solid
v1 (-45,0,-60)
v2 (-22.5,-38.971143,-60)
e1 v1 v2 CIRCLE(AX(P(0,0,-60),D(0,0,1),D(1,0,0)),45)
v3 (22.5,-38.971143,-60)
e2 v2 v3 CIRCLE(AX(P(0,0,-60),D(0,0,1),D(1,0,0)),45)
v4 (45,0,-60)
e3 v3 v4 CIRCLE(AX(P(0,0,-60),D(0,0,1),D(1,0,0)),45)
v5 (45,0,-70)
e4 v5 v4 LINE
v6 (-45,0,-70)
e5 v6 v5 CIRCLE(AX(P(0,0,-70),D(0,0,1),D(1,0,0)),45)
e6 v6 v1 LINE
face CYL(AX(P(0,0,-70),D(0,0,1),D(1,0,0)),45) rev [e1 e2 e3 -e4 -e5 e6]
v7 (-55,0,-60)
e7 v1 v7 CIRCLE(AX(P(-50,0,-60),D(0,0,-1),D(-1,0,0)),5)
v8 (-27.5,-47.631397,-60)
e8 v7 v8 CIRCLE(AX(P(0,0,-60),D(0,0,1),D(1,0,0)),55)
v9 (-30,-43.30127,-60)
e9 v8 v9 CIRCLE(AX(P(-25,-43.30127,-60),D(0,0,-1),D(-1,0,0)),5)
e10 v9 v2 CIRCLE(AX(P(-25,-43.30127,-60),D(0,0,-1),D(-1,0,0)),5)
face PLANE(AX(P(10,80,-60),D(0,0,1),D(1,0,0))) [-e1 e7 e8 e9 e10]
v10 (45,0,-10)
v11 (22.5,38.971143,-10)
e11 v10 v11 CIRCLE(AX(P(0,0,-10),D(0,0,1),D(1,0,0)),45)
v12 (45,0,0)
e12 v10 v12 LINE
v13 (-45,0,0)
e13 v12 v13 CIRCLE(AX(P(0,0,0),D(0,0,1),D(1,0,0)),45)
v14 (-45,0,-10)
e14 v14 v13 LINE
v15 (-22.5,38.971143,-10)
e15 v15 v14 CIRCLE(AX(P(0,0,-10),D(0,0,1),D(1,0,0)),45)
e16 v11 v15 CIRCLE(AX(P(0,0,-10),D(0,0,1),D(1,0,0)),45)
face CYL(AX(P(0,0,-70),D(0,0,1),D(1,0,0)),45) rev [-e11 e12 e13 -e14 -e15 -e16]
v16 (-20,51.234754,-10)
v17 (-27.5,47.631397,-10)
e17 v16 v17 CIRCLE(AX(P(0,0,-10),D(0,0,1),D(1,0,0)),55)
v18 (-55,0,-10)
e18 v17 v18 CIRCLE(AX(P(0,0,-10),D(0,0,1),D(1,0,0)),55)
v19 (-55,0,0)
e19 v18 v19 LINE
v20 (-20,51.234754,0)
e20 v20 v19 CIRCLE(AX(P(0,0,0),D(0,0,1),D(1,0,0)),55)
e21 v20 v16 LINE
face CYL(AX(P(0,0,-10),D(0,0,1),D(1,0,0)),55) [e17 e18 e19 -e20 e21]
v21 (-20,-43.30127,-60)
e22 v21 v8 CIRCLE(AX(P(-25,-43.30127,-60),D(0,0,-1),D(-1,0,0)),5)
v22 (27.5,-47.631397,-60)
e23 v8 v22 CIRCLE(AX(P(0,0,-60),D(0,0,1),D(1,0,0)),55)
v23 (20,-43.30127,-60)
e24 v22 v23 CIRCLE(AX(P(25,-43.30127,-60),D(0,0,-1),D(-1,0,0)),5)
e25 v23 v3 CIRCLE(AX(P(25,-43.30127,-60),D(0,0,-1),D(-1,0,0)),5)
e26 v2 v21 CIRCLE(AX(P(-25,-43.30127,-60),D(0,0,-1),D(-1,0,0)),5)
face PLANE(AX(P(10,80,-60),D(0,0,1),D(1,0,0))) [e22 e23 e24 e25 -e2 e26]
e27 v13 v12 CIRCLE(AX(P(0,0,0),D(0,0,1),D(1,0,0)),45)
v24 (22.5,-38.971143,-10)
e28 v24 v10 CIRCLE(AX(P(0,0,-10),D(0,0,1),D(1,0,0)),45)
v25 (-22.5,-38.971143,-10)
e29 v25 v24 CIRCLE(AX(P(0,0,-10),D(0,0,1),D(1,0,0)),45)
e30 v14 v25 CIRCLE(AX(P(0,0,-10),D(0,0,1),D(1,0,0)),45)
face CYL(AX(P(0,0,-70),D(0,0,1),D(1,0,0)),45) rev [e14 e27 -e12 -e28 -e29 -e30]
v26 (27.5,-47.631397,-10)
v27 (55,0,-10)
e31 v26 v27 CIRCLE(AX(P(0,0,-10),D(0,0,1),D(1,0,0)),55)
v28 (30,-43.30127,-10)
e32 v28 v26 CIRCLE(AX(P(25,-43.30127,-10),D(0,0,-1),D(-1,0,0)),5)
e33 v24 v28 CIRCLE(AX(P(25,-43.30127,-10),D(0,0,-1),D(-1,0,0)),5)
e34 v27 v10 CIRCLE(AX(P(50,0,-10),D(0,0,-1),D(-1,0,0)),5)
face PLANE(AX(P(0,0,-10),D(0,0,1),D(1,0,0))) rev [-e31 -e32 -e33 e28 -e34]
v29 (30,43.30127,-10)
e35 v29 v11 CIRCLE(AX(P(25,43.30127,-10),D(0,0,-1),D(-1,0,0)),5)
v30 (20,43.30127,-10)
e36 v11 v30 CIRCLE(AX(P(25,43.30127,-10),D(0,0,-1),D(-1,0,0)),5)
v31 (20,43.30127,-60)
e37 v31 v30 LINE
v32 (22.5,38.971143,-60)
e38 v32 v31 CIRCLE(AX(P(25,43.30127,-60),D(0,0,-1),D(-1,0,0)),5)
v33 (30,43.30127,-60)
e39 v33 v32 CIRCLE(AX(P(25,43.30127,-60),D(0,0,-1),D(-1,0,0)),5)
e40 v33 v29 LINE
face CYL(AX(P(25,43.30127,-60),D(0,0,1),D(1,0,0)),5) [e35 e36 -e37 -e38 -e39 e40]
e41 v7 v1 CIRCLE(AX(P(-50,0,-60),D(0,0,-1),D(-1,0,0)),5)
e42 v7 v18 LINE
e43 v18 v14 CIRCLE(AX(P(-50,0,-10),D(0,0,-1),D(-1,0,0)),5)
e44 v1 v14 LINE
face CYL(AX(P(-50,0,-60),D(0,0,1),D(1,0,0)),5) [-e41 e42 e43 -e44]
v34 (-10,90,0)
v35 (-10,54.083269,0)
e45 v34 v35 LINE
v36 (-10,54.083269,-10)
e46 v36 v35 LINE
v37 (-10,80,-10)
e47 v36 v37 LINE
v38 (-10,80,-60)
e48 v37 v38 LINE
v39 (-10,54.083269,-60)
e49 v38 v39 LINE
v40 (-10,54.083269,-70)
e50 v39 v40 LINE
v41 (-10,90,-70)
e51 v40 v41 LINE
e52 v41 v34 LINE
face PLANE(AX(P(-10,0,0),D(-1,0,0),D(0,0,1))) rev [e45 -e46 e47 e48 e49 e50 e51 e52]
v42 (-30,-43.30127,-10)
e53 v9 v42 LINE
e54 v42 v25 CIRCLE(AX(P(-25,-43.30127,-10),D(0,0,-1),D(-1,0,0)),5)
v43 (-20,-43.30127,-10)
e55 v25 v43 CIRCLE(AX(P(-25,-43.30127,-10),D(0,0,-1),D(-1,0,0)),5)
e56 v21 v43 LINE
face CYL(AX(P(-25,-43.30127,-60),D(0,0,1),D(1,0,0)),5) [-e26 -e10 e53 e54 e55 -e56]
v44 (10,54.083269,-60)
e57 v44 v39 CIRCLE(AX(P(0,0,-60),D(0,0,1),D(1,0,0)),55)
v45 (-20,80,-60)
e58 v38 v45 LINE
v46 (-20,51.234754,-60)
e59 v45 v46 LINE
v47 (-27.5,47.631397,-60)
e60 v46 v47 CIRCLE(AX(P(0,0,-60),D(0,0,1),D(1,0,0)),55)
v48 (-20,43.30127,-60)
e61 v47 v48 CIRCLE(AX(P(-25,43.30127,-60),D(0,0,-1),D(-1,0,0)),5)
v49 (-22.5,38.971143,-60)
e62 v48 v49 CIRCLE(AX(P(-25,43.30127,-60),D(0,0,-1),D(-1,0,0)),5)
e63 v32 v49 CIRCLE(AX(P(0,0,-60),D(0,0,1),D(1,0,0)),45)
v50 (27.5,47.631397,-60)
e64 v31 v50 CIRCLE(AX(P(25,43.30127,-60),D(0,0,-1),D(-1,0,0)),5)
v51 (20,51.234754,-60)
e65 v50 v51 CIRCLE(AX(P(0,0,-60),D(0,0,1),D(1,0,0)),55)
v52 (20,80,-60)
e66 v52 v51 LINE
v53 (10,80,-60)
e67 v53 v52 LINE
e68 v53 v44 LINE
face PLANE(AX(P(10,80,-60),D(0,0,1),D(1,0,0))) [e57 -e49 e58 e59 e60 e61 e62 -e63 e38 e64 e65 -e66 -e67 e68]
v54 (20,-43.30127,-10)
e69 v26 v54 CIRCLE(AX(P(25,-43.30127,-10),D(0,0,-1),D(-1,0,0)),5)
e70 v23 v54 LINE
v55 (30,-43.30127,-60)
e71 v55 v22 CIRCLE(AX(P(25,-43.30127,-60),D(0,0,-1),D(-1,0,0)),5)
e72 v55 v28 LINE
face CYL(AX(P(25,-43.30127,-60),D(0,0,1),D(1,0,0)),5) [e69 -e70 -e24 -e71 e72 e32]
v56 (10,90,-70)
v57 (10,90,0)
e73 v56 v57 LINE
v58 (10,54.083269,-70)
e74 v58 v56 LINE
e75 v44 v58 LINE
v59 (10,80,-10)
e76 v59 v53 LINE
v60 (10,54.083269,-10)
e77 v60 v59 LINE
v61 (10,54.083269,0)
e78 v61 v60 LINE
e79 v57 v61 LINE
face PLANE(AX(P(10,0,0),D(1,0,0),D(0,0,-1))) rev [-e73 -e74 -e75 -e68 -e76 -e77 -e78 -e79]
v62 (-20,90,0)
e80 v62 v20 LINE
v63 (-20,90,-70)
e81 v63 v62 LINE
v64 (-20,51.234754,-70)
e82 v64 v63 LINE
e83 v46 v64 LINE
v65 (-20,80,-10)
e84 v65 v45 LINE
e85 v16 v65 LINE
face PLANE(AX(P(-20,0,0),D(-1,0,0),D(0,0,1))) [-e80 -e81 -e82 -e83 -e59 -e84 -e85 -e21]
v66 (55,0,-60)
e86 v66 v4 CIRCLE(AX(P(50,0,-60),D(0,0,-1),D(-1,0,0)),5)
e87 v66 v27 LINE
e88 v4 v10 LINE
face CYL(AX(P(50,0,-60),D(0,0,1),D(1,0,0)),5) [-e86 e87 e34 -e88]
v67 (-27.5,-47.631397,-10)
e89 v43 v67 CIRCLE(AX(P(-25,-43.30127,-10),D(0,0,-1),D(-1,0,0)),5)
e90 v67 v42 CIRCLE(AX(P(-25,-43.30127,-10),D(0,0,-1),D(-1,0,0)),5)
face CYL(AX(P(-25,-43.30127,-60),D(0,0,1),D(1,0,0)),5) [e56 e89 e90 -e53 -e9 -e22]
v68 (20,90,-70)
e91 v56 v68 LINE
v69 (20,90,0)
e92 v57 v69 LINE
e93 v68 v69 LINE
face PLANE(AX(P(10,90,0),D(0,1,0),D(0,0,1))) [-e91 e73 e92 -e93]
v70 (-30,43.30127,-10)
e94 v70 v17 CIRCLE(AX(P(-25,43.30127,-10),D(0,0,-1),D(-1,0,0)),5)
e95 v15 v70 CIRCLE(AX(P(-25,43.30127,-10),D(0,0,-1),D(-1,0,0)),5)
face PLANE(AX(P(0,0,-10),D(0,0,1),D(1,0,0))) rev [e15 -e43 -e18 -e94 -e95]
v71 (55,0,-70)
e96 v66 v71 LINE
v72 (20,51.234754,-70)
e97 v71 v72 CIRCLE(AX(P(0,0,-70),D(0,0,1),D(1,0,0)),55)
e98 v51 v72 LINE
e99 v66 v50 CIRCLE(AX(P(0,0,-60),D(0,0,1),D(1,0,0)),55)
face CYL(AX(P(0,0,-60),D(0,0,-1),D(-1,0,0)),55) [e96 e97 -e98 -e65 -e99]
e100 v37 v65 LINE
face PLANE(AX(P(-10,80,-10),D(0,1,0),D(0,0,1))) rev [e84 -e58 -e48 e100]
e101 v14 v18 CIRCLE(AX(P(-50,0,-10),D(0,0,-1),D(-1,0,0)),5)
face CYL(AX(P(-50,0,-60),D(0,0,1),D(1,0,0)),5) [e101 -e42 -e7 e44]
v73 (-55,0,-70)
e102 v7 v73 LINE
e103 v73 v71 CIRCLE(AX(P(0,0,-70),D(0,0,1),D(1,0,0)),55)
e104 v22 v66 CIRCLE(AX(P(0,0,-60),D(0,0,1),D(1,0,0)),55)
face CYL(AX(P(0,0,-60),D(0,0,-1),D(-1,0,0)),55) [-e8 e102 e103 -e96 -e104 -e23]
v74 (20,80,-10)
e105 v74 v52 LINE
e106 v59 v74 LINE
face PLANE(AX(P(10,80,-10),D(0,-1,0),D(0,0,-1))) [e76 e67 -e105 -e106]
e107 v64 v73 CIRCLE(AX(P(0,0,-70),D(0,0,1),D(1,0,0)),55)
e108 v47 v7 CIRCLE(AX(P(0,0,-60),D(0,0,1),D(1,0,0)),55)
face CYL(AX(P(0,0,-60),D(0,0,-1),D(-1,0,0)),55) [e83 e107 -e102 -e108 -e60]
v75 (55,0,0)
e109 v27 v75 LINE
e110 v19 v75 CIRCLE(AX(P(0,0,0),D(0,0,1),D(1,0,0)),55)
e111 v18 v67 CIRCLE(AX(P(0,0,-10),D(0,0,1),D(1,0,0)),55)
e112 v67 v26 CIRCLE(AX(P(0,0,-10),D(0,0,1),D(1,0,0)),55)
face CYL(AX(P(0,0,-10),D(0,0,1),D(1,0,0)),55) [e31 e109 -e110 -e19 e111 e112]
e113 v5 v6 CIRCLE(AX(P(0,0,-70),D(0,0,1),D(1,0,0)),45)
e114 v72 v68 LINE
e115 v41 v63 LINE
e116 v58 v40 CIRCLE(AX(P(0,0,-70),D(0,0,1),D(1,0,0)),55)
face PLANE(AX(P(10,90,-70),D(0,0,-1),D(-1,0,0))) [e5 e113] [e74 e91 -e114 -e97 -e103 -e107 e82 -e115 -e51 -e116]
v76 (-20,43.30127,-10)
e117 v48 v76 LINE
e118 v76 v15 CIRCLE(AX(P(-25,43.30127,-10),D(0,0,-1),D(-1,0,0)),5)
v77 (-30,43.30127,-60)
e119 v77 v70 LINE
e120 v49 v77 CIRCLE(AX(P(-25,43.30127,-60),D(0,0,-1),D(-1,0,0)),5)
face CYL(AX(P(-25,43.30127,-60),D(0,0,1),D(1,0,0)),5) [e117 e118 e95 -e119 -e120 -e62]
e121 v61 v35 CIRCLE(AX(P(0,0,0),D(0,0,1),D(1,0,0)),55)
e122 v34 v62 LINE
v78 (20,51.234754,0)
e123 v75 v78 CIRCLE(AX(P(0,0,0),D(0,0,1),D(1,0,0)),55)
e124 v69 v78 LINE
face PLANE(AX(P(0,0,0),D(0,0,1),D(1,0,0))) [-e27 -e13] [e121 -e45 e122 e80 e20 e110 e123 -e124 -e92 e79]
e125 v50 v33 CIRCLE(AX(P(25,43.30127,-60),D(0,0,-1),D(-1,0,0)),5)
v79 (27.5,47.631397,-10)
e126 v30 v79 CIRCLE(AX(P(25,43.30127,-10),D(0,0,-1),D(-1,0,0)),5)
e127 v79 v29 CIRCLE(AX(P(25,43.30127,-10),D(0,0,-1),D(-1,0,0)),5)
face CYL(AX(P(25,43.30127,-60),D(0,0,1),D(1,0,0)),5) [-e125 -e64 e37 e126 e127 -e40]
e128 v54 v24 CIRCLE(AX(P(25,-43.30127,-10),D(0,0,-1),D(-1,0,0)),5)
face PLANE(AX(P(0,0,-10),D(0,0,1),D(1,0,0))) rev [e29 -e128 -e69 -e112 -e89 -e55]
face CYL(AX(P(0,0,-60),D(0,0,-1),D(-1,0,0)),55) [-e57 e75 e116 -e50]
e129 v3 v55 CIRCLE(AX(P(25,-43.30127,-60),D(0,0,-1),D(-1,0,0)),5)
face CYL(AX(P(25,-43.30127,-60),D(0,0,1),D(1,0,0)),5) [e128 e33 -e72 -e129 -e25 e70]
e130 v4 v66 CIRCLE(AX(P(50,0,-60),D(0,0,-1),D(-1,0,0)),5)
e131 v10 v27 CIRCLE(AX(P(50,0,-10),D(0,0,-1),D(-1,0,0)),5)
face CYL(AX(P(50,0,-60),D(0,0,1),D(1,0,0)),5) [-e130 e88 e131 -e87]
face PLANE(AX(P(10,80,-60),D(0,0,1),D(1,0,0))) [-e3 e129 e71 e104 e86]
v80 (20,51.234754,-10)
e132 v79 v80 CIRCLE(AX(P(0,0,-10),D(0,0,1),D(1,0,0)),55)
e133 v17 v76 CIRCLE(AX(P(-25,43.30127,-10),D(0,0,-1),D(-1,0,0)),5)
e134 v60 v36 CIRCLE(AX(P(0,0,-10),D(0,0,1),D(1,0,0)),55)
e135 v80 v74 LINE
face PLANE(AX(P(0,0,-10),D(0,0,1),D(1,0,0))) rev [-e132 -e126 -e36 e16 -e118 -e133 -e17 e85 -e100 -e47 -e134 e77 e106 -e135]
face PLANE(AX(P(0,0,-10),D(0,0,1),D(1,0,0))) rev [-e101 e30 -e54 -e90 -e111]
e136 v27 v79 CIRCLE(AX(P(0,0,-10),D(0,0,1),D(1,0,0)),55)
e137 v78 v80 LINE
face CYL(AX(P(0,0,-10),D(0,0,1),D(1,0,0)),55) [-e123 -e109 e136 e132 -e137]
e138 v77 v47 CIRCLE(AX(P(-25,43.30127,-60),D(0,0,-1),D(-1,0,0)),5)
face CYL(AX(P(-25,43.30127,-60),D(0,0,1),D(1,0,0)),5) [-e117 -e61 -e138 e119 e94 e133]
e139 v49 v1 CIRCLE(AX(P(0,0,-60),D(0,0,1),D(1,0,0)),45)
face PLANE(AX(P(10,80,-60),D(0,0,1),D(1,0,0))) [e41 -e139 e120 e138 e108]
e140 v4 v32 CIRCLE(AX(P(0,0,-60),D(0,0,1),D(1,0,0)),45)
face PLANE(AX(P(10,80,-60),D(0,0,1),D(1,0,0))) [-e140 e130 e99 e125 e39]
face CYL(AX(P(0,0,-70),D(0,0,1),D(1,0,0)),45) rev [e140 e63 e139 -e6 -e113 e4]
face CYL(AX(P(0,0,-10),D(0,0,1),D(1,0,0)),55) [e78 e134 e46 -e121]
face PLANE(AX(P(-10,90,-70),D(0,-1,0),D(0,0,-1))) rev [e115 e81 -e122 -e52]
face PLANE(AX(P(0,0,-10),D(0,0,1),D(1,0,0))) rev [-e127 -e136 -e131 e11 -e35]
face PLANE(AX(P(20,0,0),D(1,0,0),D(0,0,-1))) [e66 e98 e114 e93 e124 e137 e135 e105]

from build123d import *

# Parameters (mm, degrees)
FRONT_RING_PROFILE_110_R  = 55
FRONT_RING_DISC_DEPTH     = 10
REAR_RING_PROFILE_R       = 55
REAR_RING_DISC_DEPTH      = 10
RING_BORE_90_PROFILE_R    = 45
RING_BORE_90_DEPTH        = 105.642247682
FRONT_CLAMP_BRACKET_DEPTH = 10
REAR_CLAMP_BRACKET_DEPTH  = 10
CAGE_RODS_6X_10_PROFILE_R = 5
CAGE_RODS_6X_10_DEPTH     = 50


with BuildPart() as part:
    # Front Ring Profile Ø110 → Front Ring Disc (new body)
    with BuildSketch(Plane.XY):
        Circle(FRONT_RING_PROFILE_110_R)
    extrude(amount=-FRONT_RING_DISC_DEPTH)


with BuildPart() as body_2:
    # Rear Ring Profile → Rear Ring Disc (new body)
    with BuildSketch(Plane.XY.offset(-70)):
        Circle(REAR_RING_PROFILE_R)
    extrude(amount=REAR_RING_DISC_DEPTH)


with BuildPart() as ring_bore_90_tool:
    # Ring Bore Ø90 Profile → Ring Bore Ø90 (new, through all)
    with BuildSketch(Plane.XY):
        Circle(RING_BORE_90_PROFILE_R)
    extrude(amount=-RING_BORE_90_DEPTH)


with BuildPart() as part_1:
    add(part.part)

    # Ring Bore Ø90: cut by ring_bore_90_tool
    add(ring_bore_90_tool.part, mode=Mode.SUBTRACT)



with BuildPart() as body_2_1:
    add(body_2.part)

    # Ring Bore Ø90: cut by ring_bore_90_tool
    add(ring_bore_90_tool.part, mode=Mode.SUBTRACT)


with BuildPart() as part_2:
    add(part_1.part)

    add(body_2_1.part)  # Front Clamp Bracket merges body 2
    # Front Clamp Bracket Profile → Front Clamp Bracket (add)
    with BuildSketch(Plane(origin=(20, 0, 0), x_dir=(0, 0, -1), z_dir=(1, 0, 0))):
        Polygon((0, 45), (0, 90), (70, 90), (70, 45), (60, 45), (60, 80), (10, 80), (10, 45), align=None)
    extrude(amount=-FRONT_CLAMP_BRACKET_DEPTH)

    # Rear Clamp Bracket Profile → Rear Clamp Bracket (add)
    with BuildSketch(Plane(origin=(-20, 0, 0), x_dir=(0, 0, -1), z_dir=(1, 0, 0))):
        Polygon((10, 80), (60, 80), (60, 51.23475383), (70, 51.23475383), (70, 90), (0, 90), (0, 51.23475383), (10, 51.23475383), align=None)
    extrude(amount=REAR_CLAMP_BRACKET_DEPTH)

    # Cage Rods 6xØ10 Profile → Cage Rods 6xØ10 (add)
    with BuildSketch(Plane(origin=(0, 0, -10), x_dir=(-1, 0, 0), z_dir=(0, 0, -1))):
        with Locations(Location((50, 0, 0), (0, 0, 180))):
            Circle(CAGE_RODS_6X_10_PROFILE_R)
        with Locations(Location((25, -43.301270189, 0), (0, 0, 120))):
            Circle(CAGE_RODS_6X_10_PROFILE_R)
        with Locations(Location((-25, -43.301270189, 0), (0, 0, 240))):
            Circle(CAGE_RODS_6X_10_PROFILE_R)
        with Locations(Location((-50, 0, 0), (0, 0, 180))):
            Circle(CAGE_RODS_6X_10_PROFILE_R)
        with Locations(Location((-25, 43.301270189, 0), (0, 0, 120))):
            Circle(CAGE_RODS_6X_10_PROFILE_R)
        with Locations(Location((25, 43.301270189, 0), (0, 0, 240))):
            Circle(CAGE_RODS_6X_10_PROFILE_R)
    extrude(amount=CAGE_RODS_6X_10_DEPTH)


solid = part_2.part
